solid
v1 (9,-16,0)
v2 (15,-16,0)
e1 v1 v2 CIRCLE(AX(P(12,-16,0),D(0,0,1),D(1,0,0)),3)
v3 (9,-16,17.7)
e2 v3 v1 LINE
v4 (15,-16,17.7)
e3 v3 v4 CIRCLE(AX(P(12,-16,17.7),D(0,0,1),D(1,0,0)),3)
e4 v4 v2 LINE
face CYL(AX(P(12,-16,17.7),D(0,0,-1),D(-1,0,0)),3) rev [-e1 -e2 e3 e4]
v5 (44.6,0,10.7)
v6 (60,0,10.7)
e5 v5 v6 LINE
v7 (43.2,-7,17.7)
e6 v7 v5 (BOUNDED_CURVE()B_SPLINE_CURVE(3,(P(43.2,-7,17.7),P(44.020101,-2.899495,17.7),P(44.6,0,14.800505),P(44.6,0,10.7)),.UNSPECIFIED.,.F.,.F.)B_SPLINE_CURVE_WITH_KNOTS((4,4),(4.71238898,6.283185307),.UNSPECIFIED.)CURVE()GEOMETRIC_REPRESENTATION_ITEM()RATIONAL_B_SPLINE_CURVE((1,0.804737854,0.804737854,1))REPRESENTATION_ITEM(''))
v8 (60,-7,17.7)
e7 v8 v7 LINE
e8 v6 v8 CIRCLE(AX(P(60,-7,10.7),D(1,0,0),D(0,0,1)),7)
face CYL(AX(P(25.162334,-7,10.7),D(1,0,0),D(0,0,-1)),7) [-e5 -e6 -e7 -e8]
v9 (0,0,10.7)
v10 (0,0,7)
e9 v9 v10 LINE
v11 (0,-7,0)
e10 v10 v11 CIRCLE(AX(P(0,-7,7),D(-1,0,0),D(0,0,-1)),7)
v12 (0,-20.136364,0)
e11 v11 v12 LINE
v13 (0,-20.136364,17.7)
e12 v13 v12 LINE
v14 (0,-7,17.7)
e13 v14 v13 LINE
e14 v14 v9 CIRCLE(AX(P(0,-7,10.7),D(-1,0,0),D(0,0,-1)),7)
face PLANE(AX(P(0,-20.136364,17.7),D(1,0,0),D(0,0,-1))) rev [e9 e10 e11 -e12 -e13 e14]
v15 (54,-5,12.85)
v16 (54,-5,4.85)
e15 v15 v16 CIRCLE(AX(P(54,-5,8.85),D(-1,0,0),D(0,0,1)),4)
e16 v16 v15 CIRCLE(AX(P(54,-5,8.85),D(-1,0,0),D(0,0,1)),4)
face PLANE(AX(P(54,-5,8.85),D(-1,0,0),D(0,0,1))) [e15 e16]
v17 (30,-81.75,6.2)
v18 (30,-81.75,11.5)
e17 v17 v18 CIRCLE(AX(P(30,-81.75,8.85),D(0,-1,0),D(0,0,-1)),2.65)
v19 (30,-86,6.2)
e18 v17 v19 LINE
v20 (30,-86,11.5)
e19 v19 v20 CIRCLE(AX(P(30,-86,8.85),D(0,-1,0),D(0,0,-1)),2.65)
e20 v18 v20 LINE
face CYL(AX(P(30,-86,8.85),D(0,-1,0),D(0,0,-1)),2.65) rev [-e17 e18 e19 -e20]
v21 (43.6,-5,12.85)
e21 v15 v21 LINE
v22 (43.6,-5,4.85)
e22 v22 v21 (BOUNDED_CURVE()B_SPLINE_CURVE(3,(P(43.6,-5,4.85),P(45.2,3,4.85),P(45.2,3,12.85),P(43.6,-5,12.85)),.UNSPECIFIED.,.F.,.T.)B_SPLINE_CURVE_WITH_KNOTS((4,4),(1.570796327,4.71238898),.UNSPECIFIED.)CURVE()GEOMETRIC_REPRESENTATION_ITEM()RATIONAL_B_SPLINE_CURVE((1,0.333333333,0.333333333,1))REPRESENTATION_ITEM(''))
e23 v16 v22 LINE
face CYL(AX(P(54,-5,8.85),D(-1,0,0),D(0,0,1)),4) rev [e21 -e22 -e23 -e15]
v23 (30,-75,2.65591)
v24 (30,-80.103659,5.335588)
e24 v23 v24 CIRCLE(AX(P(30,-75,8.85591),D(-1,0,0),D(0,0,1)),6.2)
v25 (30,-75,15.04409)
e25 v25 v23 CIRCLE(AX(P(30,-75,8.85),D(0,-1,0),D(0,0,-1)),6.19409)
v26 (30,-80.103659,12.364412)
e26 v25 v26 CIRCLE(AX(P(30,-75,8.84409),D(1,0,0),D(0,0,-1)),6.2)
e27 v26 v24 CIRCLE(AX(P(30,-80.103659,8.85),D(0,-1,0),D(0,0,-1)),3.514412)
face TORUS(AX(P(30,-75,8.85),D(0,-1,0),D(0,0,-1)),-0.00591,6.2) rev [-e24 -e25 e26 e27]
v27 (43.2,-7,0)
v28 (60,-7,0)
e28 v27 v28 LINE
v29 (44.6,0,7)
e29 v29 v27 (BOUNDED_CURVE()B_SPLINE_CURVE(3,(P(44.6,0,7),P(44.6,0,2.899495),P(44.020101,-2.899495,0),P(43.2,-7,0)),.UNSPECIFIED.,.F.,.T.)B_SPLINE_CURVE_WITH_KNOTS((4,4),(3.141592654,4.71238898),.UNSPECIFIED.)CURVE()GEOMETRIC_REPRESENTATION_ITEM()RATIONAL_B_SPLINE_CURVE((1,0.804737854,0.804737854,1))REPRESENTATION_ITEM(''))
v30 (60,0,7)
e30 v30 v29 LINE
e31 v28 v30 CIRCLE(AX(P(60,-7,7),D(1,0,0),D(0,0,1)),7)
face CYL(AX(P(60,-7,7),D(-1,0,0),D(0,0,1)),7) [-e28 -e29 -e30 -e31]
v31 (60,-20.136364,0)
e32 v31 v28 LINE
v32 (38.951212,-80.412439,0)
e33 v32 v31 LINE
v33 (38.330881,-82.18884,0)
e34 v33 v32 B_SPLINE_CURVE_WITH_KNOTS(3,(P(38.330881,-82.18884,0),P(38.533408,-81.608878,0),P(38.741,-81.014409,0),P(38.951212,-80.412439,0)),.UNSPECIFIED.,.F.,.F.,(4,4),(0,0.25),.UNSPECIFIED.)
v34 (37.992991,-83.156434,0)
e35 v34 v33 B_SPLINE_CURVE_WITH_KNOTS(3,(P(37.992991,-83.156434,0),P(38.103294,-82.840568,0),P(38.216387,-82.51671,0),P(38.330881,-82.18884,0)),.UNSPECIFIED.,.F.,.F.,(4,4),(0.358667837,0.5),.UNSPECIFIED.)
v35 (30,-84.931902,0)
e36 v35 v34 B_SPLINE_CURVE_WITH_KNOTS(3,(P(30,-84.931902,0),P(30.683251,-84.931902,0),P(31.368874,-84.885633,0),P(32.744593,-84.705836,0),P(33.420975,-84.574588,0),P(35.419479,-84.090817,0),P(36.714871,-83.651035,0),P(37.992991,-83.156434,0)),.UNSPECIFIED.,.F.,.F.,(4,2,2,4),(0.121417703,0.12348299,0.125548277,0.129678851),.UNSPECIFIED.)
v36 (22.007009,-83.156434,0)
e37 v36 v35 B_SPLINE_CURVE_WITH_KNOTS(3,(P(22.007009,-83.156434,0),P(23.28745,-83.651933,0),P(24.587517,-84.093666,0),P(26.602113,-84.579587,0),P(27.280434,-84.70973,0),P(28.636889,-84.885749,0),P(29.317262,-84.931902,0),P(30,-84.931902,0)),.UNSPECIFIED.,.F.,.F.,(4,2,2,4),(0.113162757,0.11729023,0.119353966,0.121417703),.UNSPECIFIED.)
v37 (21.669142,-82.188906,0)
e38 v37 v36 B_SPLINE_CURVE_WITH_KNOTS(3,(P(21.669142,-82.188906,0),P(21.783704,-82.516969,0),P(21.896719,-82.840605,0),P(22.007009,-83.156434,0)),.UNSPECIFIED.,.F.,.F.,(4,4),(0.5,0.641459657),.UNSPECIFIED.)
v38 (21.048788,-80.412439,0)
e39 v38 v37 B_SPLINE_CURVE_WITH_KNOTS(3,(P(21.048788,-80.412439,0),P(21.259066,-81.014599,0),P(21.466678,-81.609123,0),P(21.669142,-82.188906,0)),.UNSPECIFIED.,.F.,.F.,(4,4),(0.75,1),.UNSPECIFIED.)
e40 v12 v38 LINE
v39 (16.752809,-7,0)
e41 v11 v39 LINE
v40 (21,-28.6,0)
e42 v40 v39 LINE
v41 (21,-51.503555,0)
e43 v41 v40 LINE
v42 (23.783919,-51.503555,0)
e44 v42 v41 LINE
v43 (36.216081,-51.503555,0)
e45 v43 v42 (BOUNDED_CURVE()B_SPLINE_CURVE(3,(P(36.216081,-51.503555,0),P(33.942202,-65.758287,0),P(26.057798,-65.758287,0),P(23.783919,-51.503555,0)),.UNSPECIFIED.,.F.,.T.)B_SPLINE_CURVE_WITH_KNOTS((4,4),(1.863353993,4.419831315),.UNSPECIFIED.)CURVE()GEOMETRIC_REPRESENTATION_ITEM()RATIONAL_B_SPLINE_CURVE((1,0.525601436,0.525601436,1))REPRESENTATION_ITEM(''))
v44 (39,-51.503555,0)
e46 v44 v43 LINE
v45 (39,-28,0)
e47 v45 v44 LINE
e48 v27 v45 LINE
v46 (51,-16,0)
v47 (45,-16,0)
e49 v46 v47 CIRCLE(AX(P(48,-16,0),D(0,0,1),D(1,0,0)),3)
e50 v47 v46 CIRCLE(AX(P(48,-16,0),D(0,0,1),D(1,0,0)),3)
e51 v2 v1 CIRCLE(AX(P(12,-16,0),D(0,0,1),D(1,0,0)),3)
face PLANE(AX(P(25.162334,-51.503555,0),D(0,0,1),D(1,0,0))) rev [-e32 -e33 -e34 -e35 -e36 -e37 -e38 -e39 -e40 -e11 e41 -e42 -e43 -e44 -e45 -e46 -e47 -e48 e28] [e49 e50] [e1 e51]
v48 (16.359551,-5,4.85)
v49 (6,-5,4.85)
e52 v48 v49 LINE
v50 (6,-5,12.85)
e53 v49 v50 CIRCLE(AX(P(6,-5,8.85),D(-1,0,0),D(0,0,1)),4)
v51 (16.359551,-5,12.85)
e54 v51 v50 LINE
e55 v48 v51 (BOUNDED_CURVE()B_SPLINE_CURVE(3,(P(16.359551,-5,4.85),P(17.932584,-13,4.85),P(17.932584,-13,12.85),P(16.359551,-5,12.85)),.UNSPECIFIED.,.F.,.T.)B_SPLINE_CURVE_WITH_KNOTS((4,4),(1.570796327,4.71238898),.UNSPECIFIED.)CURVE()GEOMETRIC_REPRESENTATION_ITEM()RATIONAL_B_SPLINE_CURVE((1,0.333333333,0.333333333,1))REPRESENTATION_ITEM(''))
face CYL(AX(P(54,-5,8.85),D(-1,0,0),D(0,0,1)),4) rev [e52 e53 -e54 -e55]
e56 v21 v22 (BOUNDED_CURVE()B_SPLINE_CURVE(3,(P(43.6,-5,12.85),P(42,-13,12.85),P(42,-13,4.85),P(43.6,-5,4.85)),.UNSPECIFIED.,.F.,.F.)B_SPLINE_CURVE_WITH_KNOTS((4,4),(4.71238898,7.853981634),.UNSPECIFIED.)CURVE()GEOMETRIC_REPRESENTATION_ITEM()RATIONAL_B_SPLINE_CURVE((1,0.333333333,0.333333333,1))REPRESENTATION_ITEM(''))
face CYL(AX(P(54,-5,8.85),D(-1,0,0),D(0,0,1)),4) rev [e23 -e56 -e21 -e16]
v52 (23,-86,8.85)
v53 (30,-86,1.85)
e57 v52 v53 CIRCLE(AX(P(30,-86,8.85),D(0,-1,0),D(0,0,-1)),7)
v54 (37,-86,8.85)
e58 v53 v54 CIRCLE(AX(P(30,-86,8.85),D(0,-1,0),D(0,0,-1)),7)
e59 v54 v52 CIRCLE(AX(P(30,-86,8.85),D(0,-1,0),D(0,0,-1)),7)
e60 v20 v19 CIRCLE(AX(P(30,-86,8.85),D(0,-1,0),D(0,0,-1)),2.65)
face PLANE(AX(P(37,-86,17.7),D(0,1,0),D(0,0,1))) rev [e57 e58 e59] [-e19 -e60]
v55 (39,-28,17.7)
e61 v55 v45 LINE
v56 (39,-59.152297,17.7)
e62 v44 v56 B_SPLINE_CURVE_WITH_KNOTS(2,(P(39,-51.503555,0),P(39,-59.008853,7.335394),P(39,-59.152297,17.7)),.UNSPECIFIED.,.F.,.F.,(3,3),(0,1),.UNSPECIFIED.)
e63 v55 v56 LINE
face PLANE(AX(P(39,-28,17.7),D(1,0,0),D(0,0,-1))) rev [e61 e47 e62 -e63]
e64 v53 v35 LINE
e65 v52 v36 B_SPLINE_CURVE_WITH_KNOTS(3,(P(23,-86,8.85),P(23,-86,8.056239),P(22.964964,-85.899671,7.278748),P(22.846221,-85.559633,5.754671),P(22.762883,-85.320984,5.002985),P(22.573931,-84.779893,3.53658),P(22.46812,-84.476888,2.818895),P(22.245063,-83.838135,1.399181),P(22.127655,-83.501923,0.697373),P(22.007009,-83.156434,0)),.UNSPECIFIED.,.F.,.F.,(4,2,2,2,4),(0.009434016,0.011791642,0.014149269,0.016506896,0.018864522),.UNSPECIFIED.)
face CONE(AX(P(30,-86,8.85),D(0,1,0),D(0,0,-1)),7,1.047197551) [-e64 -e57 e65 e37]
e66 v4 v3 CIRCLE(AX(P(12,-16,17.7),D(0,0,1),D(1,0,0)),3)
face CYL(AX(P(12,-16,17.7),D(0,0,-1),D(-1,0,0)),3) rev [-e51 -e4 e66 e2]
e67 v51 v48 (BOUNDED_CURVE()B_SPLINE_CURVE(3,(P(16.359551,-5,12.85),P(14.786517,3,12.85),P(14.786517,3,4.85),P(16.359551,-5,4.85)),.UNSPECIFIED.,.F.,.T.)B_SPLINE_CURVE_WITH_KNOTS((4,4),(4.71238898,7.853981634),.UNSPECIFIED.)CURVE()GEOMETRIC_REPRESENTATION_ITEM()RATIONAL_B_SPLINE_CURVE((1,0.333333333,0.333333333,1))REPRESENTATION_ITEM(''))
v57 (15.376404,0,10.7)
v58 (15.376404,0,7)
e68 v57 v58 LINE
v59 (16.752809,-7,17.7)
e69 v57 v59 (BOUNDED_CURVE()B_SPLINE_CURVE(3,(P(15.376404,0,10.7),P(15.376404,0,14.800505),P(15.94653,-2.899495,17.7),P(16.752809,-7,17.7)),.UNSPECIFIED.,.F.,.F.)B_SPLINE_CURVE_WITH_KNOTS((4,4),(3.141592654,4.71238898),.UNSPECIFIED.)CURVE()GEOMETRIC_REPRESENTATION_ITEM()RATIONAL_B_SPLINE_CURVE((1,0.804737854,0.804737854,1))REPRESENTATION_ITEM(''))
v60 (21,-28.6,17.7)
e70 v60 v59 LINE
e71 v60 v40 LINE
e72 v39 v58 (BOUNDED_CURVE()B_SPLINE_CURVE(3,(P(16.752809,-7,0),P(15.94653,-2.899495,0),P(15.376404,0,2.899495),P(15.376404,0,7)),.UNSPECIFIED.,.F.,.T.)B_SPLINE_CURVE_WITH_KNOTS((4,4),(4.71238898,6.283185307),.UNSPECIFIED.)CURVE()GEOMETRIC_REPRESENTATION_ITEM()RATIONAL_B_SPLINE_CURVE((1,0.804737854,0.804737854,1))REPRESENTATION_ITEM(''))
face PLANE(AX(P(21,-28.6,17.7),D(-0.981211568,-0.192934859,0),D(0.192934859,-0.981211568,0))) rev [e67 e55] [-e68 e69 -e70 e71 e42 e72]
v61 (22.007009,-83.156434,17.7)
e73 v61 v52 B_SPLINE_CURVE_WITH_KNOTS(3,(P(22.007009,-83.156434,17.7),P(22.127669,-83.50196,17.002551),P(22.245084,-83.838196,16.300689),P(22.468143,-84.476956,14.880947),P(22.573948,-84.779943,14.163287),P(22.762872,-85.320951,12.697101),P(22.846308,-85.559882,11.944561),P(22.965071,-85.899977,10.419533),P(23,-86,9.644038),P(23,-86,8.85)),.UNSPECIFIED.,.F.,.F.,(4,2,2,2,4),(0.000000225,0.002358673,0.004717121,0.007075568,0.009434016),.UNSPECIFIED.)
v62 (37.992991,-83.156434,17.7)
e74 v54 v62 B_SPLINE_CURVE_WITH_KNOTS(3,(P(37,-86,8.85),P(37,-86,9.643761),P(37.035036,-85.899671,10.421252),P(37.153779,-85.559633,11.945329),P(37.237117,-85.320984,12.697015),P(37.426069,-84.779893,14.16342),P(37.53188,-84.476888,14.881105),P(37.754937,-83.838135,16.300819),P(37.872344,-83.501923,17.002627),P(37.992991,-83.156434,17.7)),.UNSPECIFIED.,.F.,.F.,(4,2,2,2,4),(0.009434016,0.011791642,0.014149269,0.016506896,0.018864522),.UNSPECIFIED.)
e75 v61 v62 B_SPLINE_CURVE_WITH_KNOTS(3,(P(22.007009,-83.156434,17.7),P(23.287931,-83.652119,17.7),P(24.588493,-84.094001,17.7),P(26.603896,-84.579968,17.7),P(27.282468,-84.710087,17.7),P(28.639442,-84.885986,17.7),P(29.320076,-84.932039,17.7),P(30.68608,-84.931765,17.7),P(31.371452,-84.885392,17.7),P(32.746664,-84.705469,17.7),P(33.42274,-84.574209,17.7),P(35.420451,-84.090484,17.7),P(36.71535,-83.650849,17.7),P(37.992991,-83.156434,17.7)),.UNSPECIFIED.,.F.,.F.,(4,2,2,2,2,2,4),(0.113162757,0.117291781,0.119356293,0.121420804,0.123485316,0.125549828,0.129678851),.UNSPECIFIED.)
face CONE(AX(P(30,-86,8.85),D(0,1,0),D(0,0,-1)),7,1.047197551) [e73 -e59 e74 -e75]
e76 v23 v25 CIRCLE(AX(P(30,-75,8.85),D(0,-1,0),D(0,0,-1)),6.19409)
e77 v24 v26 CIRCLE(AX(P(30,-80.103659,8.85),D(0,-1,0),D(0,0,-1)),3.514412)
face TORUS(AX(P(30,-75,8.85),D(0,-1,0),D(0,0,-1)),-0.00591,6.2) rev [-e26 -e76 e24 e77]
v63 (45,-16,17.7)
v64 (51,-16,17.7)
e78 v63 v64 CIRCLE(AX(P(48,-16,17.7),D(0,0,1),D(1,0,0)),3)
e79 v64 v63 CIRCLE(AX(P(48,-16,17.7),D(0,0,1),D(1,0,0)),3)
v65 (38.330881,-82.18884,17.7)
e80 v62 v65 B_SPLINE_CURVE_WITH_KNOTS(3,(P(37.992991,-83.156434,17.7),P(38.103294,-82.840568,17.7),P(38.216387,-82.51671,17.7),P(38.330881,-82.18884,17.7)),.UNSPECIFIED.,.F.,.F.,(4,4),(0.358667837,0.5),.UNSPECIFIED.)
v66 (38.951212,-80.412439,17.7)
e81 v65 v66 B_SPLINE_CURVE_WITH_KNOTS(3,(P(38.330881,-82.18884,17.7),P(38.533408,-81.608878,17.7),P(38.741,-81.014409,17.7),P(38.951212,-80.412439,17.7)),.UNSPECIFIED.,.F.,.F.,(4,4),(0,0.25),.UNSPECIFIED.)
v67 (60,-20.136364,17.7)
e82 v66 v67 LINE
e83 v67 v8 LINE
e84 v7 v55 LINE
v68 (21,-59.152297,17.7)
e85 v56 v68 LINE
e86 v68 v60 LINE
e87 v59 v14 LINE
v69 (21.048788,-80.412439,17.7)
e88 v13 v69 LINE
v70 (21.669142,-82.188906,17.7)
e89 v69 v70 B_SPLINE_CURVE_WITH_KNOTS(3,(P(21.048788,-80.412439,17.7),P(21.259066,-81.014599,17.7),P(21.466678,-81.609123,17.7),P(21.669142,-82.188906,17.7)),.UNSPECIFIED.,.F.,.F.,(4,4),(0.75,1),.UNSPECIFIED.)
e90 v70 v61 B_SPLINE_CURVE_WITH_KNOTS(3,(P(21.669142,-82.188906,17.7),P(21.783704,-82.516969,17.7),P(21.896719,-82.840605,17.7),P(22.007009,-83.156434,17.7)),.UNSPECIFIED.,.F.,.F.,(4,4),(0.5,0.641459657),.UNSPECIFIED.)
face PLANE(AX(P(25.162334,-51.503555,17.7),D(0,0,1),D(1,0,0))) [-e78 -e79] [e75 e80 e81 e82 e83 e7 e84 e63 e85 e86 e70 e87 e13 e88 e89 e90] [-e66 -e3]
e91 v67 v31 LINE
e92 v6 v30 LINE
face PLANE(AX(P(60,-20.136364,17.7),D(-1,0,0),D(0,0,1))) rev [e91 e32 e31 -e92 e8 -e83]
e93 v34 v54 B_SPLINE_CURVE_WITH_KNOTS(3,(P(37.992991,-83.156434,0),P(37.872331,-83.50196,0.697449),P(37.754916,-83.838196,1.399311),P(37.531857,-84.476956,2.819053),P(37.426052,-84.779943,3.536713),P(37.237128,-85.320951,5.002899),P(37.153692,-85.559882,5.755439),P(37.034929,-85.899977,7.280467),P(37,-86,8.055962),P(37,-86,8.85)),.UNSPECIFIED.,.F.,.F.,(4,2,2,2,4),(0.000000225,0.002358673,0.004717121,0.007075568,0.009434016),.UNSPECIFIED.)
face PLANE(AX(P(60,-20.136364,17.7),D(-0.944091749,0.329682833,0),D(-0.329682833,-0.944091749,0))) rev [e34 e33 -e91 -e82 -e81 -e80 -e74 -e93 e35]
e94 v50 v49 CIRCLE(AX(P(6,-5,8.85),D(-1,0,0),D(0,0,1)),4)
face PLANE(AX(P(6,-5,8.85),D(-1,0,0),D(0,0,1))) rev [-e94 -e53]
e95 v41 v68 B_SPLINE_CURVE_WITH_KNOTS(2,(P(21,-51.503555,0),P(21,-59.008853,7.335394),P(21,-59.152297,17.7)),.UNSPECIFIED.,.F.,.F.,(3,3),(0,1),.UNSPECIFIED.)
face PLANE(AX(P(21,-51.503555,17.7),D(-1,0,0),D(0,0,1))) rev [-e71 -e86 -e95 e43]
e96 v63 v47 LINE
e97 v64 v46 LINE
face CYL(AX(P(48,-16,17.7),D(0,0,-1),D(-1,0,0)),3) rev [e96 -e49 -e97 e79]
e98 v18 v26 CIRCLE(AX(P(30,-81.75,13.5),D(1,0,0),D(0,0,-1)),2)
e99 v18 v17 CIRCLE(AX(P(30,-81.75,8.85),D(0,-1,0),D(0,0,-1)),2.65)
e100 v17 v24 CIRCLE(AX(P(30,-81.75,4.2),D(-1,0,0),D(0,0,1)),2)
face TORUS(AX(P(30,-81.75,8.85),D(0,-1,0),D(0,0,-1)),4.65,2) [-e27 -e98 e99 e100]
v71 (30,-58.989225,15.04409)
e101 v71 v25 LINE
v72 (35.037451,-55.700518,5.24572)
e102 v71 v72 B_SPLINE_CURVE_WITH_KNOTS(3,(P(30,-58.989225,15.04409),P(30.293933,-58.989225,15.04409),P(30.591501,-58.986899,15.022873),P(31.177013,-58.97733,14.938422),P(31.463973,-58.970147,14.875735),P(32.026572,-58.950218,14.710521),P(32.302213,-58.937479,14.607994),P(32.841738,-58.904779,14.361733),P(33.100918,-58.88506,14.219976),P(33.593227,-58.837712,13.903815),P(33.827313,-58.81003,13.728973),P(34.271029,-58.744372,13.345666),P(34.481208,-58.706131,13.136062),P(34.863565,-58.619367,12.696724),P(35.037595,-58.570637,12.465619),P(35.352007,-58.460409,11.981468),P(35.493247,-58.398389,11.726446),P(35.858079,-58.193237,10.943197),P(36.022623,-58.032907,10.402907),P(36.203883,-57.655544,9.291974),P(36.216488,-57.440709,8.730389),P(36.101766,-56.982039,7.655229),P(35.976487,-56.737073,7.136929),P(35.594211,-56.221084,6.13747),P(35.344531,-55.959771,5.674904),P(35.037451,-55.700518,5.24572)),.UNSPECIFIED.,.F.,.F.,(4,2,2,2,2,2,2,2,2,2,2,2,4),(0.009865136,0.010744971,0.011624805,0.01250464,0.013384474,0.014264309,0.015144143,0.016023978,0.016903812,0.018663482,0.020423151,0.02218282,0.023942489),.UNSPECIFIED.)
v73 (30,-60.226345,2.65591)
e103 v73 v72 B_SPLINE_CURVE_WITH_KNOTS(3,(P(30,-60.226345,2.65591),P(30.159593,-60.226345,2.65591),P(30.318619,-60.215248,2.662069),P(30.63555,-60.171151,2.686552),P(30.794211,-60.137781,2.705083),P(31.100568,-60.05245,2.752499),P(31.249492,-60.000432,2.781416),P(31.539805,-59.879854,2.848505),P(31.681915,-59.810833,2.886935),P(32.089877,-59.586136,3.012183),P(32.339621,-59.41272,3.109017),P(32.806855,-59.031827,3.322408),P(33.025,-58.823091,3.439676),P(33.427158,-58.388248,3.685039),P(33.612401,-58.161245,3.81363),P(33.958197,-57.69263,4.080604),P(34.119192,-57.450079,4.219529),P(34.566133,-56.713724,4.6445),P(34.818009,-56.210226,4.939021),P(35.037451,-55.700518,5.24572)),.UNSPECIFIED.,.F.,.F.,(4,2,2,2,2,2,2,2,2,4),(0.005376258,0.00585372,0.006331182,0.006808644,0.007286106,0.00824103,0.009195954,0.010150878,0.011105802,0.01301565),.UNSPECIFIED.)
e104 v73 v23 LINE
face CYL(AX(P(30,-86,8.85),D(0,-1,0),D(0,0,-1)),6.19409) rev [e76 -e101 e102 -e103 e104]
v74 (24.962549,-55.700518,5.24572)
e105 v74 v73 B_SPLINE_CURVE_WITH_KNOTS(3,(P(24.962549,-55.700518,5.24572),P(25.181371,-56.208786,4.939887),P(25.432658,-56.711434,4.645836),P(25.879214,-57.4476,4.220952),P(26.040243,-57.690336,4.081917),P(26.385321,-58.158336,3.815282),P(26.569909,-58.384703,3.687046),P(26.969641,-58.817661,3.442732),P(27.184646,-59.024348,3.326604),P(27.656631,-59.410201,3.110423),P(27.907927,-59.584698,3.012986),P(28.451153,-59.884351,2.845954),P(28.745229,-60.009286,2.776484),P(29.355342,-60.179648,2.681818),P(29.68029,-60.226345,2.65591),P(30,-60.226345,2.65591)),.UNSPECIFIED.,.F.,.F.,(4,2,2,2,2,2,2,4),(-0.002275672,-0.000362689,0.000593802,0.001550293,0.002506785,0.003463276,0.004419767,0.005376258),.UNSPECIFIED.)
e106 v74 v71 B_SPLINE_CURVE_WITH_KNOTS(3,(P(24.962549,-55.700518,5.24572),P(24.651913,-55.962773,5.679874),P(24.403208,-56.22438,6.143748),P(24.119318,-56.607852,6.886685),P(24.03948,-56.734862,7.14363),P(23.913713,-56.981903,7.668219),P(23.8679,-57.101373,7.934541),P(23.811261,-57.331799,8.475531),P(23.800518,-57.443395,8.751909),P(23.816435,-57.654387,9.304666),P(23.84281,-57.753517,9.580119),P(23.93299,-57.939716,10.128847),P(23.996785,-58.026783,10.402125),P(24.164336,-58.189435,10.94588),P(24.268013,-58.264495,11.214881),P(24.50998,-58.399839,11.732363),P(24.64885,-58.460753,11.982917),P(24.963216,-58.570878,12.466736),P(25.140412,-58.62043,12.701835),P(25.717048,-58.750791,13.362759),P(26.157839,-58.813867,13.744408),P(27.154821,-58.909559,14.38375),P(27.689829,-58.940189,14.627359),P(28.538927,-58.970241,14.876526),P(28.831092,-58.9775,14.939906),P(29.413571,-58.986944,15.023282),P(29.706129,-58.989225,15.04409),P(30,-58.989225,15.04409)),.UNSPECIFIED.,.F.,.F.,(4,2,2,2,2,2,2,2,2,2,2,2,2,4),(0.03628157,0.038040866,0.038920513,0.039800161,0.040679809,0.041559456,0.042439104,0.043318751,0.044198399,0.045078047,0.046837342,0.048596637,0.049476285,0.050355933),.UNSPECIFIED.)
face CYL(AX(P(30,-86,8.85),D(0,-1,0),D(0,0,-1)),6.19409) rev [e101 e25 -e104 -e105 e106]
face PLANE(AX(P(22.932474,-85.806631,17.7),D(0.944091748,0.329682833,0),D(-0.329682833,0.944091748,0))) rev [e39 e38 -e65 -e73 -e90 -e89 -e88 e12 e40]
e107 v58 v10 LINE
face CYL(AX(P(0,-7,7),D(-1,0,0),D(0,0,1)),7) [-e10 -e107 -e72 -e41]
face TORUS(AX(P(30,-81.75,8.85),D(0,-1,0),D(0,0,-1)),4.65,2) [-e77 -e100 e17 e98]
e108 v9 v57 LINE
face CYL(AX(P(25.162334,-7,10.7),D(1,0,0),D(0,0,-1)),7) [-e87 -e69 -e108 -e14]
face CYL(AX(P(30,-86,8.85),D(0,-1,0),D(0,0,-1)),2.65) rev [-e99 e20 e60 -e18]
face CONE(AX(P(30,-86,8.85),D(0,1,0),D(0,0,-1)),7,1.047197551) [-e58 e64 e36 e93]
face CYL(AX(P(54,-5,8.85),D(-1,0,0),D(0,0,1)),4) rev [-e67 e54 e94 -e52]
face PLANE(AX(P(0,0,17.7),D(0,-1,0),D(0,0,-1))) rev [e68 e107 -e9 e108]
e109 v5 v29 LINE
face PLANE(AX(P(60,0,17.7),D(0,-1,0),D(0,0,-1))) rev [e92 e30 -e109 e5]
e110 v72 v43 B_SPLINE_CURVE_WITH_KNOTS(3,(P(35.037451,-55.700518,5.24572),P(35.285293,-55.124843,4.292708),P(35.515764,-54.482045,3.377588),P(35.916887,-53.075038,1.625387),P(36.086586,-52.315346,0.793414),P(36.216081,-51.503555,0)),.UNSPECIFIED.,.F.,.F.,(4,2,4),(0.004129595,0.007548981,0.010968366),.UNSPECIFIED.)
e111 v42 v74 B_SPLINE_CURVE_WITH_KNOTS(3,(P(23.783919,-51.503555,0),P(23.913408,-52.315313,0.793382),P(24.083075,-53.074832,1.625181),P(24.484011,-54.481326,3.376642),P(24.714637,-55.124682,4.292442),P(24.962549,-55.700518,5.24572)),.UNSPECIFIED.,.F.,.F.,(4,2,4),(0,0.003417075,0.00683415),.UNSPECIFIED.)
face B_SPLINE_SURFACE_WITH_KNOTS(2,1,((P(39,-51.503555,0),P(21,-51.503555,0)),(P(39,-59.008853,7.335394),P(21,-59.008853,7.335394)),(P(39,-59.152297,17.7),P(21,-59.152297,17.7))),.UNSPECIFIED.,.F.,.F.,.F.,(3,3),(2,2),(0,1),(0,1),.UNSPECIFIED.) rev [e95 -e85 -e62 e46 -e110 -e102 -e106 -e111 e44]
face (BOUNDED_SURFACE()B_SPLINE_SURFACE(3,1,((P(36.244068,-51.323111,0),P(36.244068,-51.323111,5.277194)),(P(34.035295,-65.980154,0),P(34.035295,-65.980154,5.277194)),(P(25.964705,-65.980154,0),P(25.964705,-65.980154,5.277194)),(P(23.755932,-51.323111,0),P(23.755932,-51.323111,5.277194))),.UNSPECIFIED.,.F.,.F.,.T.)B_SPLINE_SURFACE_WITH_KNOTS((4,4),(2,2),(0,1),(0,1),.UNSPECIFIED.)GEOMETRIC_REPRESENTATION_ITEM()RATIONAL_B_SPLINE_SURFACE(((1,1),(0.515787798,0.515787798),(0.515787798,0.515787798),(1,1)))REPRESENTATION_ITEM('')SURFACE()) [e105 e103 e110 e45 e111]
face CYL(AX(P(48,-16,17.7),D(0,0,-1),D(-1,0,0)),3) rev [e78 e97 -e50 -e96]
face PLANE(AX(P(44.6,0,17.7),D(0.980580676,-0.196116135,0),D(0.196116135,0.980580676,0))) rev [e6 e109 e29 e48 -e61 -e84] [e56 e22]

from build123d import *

# Parameters (mm, degrees)
SKETCH1_R                      = 3
BOSS_EXTRUDE2_DEPTH            = 17.7
CUT_EXTRUDE1_REACH             = 94.786
CUT_EXTRUDE1_DIRECTION_2_REACH = 94.786
SKETCH6_RX                     = 12.258033
SKETCH6_RY                     = 6.491927
CUT_EXTRUDE2_DEPTH             = 48.7
SKETCH7_R                      = 6.19409
CUT_EXTRUDE3_DEPTH             = 60.7
SKETCH8_R                      = 4
CUT_EXTRUDE4_DEPTH             = 48
FILLET1_R                      = 7
SKETCH10_OUTSIDE_W             = 249.546
SKETCH10_OUTSIDE_H             = 207.246
SKETCH10_OUTSIDE_R             = 7
CUT_EXTRUDE5_DEPTH             = 48
CUT_EXTRUDE5_TAPER             = 60


with BuildPart() as part:
    # Sketch1 → Boss-Extrude2 (new body)
    with BuildSketch(Plane.XY):
        with BuildLine():
            Line((39, -51.503555), (34.837666, -51.503555))
            Line((34.837666, -51.503555), (25.162334, -51.503555))
            Line((25.162334, -51.503555), (21, -51.503555))
            Line((21, -51.503555), (21, -28.6))
            Line((21, -28.6), (15.376404, 0))
            Line((15.376404, 0), (0, 0))
            Line((0, 0), (0, -20.136364))
            Line((0, -20.136364), (21.048788, -80.412439))
            add(Edge.make_bspline(
                [(21.669142, -82.188906), (21.466678, -81.609123), (21.259066, -81.014599), (21.048788, -80.412439)],
                knots=[0.75, 0.75, 0.75, 0.75, 1, 1, 1, 1], degree=3))
            add(Edge.make_bspline(
                [(22.255532, -83.868113), (22.06924, -83.334643), (21.871606, -82.768689), (21.669142, -82.188906)],
                knots=[0.5, 0.5, 0.5, 0.5, 0.75, 0.75, 0.75, 0.75], degree=3))
            add(Edge.make_bspline(
                [(22.524034, -84.637007), (22.439154, -84.393941), (22.348677, -84.134848), (22.255532, -83.868113)],
                knots=[0.375, 0.375, 0.375, 0.375, 0.5, 0.5, 0.5, 0.5], degree=3))
            add(Edge.make_bspline(
                [(22.758263, -85.307753), (22.688292, -85.107381), (22.608914, -84.880073), (22.524034, -84.637007)],
                knots=[0.25, 0.25, 0.25, 0.25, 0.375, 0.375, 0.375, 0.375], degree=3))
            add(Edge.make_bspline(
                [(22.855261, -85.585519), (22.825847, -85.50129), (22.793248, -85.407938), (22.758263, -85.307753)],
                knots=[0.1875, 0.1875, 0.1875, 0.1875, 0.25, 0.25, 0.25, 0.25], degree=3))
            add(Edge.make_bspline(
                [(22.932474, -85.806631), (22.910958, -85.745015), (22.884674, -85.669748), (22.855261, -85.585519)],
                knots=[0.125, 0.125, 0.125, 0.125, 0.1875, 0.1875, 0.1875, 0.1875], degree=3))
            add(Edge.make_bspline(
                [(23, -86), (22.975508, -85.929864), (22.932474, -85.806631)],
                knots=[0, 0, 0, 0.125, 0.125, 0.125], degree=2))
            Line((23, -86), (37, -86))
            add(Edge.make_bspline(
                [(37.068167, -85.804796), (37.025162, -85.927946), (37, -86)],
                knots=[0.875, 0.875, 0.875, 1, 1, 1], degree=2))
            add(Edge.make_bspline(
                [(37.242328, -85.306061), (37.171936, -85.507639), (37.111171, -85.681646), (37.068167, -85.804796)],
                knots=[0.75, 0.75, 0.75, 0.75, 0.875, 0.875, 0.875, 0.875], degree=3))
            add(Edge.make_bspline(
                [(37.47673, -84.63482), (37.392157, -84.877005), (37.31272, -85.104482), (37.242328, -85.306061)],
                knots=[0.625, 0.625, 0.625, 0.625, 0.75, 0.75, 0.75, 0.75], degree=3))
            add(Edge.make_bspline(
                [(37.744144, -83.869041), (37.651111, -84.135454), (37.561302, -84.392634), (37.47673, -84.63482)],
                knots=[0.5, 0.5, 0.5, 0.5, 0.625, 0.625, 0.625, 0.625], degree=3))
            add(Edge.make_bspline(
                [(38.330881, -82.18884), (38.128355, -82.768803), (37.930211, -83.336215), (37.744144, -83.869041)],
                knots=[0.25, 0.25, 0.25, 0.25, 0.5, 0.5, 0.5, 0.5], degree=3))
            add(Edge.make_bspline(
                [(38.951212, -80.412439), (38.741, -81.014409), (38.533408, -81.608878), (38.330881, -82.18884)],
                knots=[0, 0, 0, 0, 0.25, 0.25, 0.25, 0.25], degree=3))
            Line((38.951212, -80.412439), (60, -20.136364))
            Line((60, -20.136364), (60, 0))
            Line((60, 0), (44.6, 0))
            Line((44.6, 0), (39, -28))
            Line((39, -28), (39, -51.503555))
        make_face()
        with Locations((48, -16)):
            Circle(SKETCH1_R, mode=Mode.SUBTRACT)
        with Locations((12, -16)):
            Circle(SKETCH1_R, mode=Mode.SUBTRACT)
    extrude(amount=BOSS_EXTRUDE2_DEPTH)

    # Sketch2 → Cut-Revolve2 (revolve, cut)
    with BuildSketch(Plane.ZY.offset(-30), mode=Mode.PRIVATE) as cut_revolve2_sk:
        with BuildLine():
            ThreePointArc((11.5, -81.75), (11.729241, -80.820262), (12.364412, -80.103659))
            ThreePointArc((12.364412, -80.103659), (14.333443, -77.882187), (15.04409, -75))
            Line((15.04409, -75), (15.04409, -57.48))
            Line((15.04409, -57.48), (8.85, -57.48))
            Line((8.85, -57.48), (8.85, -86))
            Line((8.85, -86), (11.5, -86))
            Line((11.5, -86), (11.5, -81.75))
        make_face()
    revolve(cut_revolve2_sk.sketch.rotate(Axis((30, -86, 8.85), (0, 1, 0)), 180), axis=Axis((30, -86, 8.85), (0, 1, 0)), mode=Mode.SUBTRACT)

    # Cut-Extrude1: up to this face of the body (flat: up to its plane)
    cut_extrude1_end = Plane(part.part.faces().sort_by_distance((39, -39.751777, 8.85))[0])
    # Sketch3 → Cut-Extrude1 (cut, up to the picked face)
    with BuildSketch(Plane.ZY.offset(-30), mode=Mode.PRIVATE) as cut_extrude1_sk1:
        with BuildLine():
            Line((0, -51.503555), (17.7, -51.503555))
            Line((17.7, -51.503555), (17.7, -59.152297))
            add(Edge.make_bspline(
                [(17.7, -59.152297), (7.335394, -59.008853), (0, -51.503555)],
                knots=[0, 0, 0, 1, 1, 1], degree=2))
        make_face()
    cut_extrude1_tool1 = split(extrude(cut_extrude1_sk1.sketch, amount=-CUT_EXTRUDE1_REACH, mode=Mode.PRIVATE), bisect_by=cut_extrude1_end, keep=Keep.BOTH, mode=Mode.PRIVATE)
    add(cut_extrude1_tool1.solids().sort_by(Axis((30, -54.604638, 10.907898), (1, 0, 0)))[0], mode=Mode.SUBTRACT)

    # Cut-Extrude1 direction 2: up to this face of the body (flat: up to its plane)
    cut_extrude1_direction_2_end = Plane(part.part.faces().sort_by_distance((21, -40.051777, 8.85))[0])
    # Sketch3 → Cut-Extrude1 direction 2 (cut, up to the picked face)
    with BuildSketch(Plane.ZY.offset(-30), mode=Mode.PRIVATE) as cut_extrude1_direction_2_sk1:
        with BuildLine():
            Line((0, -51.503555), (17.7, -51.503555))
            Line((17.7, -51.503555), (17.7, -59.152297))
            add(Edge.make_bspline(
                [(17.7, -59.152297), (7.335394, -59.008853), (0, -51.503555)],
                knots=[0, 0, 0, 1, 1, 1], degree=2))
        make_face()
    cut_extrude1_direction_2_tool1 = split(extrude(cut_extrude1_direction_2_sk1.sketch, amount=CUT_EXTRUDE1_DIRECTION_2_REACH, mode=Mode.PRIVATE), bisect_by=cut_extrude1_direction_2_end, keep=Keep.BOTH, mode=Mode.PRIVATE)
    add(cut_extrude1_direction_2_tool1.solids().sort_by(Axis((30, -54.604638, 10.907898), (-1, 0, 0)))[0], mode=Mode.SUBTRACT)

    # Sketch6 → Cut-Extrude2 (cut)
    with BuildSketch(Plane(origin=(0, 0, 8.85), x_dir=(-1, 0, 0), z_dir=(0, 0, -1))):
        with Locations(Location((-30, -47.968312), (0, 0, 90))):
            Ellipse(SKETCH6_RX, SKETCH6_RY)
    extrude(amount=CUT_EXTRUDE2_DEPTH, mode=Mode.SUBTRACT)

    # Sketch7 → Cut-Extrude3 (cut)
    with BuildSketch(Plane(origin=(0, 0, 0), x_dir=(1, 0, 0), z_dir=(0, 1, 0))):
        with Locations(Location((30, -8.85, 0), (0, 0, 90))):
            Circle(SKETCH7_R)
    extrude(amount=-CUT_EXTRUDE3_DEPTH, mode=Mode.SUBTRACT)

    # Sketch8 → Cut-Extrude4 (cut)
    with BuildSketch(Plane.ZY.offset(-6)):
        with Locations((8.85, -5)):
            Circle(SKETCH8_R)
    extrude(amount=-CUT_EXTRUDE4_DEPTH, mode=Mode.SUBTRACT)

    # Fillet1
    fillet1_edges = [part.edges().sort_by_distance(p)[0] for p in [
        (7.688202, 0, 17.7),
        (52.3, 0, 0),
        (7.688202, 0, 0),
        (52.3, 0, 17.7),
    ]]
    fillet(fillet1_edges, radius=FILLET1_R)

    # Sketch10 outside → Cut-Extrude5 (cut)
    with BuildSketch(Plane.XZ.offset(86)):
        with Locations((30, 8.85)):
            Rectangle(SKETCH10_OUTSIDE_W, SKETCH10_OUTSIDE_H)
        with Locations((30, 8.85)):
            Circle(SKETCH10_OUTSIDE_R, mode=Mode.SUBTRACT)
    extrude(amount=-CUT_EXTRUDE5_DEPTH, taper=CUT_EXTRUDE5_TAPER, mode=Mode.SUBTRACT)


solid = part.part
